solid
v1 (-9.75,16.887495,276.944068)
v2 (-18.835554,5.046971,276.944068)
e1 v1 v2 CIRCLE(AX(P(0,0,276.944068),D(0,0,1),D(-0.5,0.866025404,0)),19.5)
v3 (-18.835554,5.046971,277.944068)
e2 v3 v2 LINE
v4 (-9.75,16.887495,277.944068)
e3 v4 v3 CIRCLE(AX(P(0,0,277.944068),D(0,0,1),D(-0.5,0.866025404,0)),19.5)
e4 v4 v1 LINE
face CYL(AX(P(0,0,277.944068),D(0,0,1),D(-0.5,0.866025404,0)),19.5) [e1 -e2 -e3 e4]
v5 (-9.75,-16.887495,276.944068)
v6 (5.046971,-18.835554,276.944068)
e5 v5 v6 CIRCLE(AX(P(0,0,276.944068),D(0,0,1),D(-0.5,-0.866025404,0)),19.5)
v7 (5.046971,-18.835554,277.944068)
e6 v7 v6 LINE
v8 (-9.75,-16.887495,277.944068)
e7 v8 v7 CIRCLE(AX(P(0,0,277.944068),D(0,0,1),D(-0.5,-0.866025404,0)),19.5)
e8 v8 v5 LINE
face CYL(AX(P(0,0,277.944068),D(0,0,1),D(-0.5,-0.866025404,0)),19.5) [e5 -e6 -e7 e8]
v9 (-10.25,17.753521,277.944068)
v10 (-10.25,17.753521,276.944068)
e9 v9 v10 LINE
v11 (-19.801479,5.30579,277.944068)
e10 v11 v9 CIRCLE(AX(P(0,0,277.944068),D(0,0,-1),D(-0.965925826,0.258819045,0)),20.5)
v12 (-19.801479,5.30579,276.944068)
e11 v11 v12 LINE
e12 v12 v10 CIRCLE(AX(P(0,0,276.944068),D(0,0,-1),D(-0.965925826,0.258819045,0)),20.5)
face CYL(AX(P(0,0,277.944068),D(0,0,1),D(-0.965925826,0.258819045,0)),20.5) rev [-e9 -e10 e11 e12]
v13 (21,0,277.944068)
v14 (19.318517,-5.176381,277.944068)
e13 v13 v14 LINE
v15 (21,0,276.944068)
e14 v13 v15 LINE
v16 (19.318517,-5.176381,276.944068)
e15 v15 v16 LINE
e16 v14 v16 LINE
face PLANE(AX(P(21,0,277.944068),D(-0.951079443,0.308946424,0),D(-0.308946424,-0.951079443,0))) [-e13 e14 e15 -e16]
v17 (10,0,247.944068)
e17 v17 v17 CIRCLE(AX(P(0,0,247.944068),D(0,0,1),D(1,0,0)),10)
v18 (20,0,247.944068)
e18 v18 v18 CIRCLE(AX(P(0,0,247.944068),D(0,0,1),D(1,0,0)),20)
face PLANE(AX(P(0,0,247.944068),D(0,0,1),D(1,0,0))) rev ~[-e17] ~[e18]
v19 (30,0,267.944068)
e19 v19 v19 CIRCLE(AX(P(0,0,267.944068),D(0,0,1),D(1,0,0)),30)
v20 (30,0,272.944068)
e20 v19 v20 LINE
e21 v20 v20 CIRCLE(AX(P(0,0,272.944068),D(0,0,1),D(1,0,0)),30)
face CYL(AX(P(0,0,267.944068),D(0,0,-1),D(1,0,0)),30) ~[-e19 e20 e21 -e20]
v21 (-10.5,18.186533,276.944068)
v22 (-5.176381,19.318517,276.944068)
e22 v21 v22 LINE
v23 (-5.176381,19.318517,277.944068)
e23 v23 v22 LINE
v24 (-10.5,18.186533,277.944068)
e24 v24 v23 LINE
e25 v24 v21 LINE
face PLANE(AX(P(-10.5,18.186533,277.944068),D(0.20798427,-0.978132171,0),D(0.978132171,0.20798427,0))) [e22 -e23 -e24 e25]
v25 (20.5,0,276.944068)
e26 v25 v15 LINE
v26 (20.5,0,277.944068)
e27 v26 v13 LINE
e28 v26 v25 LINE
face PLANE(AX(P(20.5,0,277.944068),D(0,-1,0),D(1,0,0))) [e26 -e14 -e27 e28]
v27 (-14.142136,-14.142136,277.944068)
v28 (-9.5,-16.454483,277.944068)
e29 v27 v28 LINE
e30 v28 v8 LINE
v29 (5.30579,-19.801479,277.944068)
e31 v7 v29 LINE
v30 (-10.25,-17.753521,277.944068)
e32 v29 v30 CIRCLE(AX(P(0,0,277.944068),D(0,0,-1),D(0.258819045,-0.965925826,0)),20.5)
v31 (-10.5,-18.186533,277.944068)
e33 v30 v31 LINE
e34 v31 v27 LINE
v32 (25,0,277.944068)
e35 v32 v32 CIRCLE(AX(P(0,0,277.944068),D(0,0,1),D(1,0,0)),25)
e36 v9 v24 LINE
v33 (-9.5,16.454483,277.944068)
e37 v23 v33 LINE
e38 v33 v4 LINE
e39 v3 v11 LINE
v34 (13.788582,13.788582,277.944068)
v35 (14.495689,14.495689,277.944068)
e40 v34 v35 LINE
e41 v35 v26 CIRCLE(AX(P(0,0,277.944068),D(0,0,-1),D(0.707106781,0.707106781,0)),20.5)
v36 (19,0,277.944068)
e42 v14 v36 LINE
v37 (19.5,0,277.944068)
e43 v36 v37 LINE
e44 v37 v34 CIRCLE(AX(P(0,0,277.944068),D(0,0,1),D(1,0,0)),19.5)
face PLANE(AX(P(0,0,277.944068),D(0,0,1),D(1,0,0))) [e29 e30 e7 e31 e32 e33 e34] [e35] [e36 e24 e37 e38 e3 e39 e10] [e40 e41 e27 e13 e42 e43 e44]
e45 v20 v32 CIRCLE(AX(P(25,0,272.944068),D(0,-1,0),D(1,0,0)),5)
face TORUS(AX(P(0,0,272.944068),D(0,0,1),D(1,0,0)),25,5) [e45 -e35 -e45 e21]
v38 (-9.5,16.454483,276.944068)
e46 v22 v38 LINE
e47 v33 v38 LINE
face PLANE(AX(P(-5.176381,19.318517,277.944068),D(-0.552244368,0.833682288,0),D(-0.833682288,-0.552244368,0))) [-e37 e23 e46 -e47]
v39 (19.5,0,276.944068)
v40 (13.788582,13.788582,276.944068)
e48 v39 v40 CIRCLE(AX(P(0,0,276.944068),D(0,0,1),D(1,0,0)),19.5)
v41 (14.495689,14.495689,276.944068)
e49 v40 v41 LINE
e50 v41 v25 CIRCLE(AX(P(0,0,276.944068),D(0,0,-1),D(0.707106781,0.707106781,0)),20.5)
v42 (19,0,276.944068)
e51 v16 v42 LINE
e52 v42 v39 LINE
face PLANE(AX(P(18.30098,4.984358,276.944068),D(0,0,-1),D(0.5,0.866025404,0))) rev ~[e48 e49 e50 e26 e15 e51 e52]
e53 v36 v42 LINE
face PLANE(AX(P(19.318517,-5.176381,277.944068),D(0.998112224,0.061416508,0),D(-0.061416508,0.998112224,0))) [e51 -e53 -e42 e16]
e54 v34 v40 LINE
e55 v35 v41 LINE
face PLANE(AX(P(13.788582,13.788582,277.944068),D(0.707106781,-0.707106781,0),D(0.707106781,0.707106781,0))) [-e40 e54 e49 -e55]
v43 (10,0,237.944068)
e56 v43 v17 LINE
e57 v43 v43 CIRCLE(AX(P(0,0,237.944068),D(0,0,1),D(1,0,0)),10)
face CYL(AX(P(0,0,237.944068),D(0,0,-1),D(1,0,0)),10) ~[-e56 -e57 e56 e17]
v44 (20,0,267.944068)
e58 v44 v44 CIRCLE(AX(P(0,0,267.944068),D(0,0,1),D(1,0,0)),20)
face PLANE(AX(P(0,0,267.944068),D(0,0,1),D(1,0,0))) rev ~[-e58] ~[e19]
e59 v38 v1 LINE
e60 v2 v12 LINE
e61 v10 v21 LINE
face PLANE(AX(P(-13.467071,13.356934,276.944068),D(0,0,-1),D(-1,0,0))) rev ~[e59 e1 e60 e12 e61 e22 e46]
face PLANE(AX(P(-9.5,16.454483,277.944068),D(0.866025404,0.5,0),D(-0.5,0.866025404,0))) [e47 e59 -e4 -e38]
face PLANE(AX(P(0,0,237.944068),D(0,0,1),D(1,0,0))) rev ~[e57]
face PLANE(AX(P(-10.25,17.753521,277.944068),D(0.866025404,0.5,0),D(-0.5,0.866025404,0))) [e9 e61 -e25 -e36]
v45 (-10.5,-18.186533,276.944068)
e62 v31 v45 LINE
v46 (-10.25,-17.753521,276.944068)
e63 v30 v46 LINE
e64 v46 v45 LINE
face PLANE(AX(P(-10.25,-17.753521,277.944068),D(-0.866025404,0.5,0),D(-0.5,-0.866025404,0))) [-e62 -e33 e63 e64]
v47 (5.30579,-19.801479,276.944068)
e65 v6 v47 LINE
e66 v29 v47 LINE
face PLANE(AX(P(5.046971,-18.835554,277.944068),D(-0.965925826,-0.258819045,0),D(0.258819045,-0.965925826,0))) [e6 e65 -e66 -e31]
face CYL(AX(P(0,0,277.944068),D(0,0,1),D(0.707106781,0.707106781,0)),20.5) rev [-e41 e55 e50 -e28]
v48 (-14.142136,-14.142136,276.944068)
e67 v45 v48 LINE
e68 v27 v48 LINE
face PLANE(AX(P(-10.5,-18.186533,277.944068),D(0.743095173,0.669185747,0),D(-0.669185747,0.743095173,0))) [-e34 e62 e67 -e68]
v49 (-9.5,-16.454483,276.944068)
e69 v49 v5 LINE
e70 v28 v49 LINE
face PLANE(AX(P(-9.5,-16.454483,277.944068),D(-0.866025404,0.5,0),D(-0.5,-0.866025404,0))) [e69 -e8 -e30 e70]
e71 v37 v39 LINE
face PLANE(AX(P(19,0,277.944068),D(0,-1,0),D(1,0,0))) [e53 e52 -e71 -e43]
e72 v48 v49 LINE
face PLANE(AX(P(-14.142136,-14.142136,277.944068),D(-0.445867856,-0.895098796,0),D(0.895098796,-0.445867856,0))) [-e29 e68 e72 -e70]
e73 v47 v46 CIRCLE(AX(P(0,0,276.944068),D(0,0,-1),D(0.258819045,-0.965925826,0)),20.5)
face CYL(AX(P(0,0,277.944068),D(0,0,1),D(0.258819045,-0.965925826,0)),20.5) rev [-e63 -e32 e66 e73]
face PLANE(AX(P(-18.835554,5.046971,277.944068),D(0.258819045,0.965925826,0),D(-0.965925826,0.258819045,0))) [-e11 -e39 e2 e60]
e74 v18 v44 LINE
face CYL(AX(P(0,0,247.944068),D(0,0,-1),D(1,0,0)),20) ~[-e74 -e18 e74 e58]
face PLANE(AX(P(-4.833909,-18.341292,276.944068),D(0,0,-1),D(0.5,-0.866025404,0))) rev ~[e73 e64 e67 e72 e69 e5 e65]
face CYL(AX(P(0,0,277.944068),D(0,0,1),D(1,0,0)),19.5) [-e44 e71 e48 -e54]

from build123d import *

# Parameters (mm, degrees)
SKETCH_1_R               = 100
EXTRUDE_1_DEPTH          = 100
SKETCH_2_R               = 200
EXTRUDE_2_DEPTH          = 200
SKETCH_3_R               = 300
EXTRUDE_3_DEPTH          = 100
CUT_EXTRUDE_1_DEPTH      = 10
PATTERN_CIRCULAR_1_COUNT = 3
FILLET_1_R               = 50
SCALE_1_SCALE            = 0.1


with BuildPart() as part:
    # 草图1 → 凸台-拉伸1 (new body)
    with BuildSketch(Plane.XY):
        Circle(SKETCH_1_R)
    extrude(amount=EXTRUDE_1_DEPTH)

    # 草图2 → 凸台-拉伸2 (add)
    with BuildSketch(Plane.XY.offset(100)):
        Circle(SKETCH_2_R)
    extrude(amount=EXTRUDE_2_DEPTH)

    # 草图3 → 凸台-拉伸3 (add)
    with BuildSketch(Plane.XY.offset(300)):
        Circle(SKETCH_3_R)
    extrude(amount=EXTRUDE_3_DEPTH)

    # 草图4 → 切除-拉伸1 (cut)
    with BuildSketch(Plane.XY.offset(400)):
        with BuildLine():
            Line((-188.355536126, 50.469713795), (-198.014794389, 53.057904246))
            ThreePointArc((-198.014794389, 53.057904246), (-162.63743476, 124.796092947), (-102.5, 177.535207776))
            Line((-102.5, 177.535207776), (-105, 181.865334795))
            Line((-105, 181.865334795), (-51.763809021, 193.185165258))
            Line((-51.763809021, 193.185165258), (-95, 164.544826719))
            Line((-95, 164.544826719), (-97.5, 168.874953738))
            ThreePointArc((-97.5, 168.874953738), (-154.703901357, 118.708478657), (-188.355536126, 50.469713795))
        make_face()
    cut_extrude_1 = extrude(amount=-CUT_EXTRUDE_1_DEPTH, mode=Mode.SUBTRACT)

    # 阵列(圆周)1: 切除-拉伸1 ×3 about axis
    pattern_circular_1_axis = Axis((0, 0, 0), (0, 0, 1))
    for i in range(1, PATTERN_CIRCULAR_1_COUNT):
        add(cut_extrude_1.rotate(pattern_circular_1_axis, i * 360 / PATTERN_CIRCULAR_1_COUNT), mode=Mode.SUBTRACT)

    # 圆角1
    fillet_1_edges = [part.edges().sort_by_distance(p)[0] for p in [
        (-300, 0, 400),
    ]]
    fillet(fillet_1_edges, radius=FILLET_1_R)


with BuildPart() as part_1:
    # 缩放比例1: scaled about (0, 0, 264.382298041)
    add(part.part.scale(SCALE_1_SCALE).moved(Location((0, 0, 237.944068237))))


solid = part_1.part
